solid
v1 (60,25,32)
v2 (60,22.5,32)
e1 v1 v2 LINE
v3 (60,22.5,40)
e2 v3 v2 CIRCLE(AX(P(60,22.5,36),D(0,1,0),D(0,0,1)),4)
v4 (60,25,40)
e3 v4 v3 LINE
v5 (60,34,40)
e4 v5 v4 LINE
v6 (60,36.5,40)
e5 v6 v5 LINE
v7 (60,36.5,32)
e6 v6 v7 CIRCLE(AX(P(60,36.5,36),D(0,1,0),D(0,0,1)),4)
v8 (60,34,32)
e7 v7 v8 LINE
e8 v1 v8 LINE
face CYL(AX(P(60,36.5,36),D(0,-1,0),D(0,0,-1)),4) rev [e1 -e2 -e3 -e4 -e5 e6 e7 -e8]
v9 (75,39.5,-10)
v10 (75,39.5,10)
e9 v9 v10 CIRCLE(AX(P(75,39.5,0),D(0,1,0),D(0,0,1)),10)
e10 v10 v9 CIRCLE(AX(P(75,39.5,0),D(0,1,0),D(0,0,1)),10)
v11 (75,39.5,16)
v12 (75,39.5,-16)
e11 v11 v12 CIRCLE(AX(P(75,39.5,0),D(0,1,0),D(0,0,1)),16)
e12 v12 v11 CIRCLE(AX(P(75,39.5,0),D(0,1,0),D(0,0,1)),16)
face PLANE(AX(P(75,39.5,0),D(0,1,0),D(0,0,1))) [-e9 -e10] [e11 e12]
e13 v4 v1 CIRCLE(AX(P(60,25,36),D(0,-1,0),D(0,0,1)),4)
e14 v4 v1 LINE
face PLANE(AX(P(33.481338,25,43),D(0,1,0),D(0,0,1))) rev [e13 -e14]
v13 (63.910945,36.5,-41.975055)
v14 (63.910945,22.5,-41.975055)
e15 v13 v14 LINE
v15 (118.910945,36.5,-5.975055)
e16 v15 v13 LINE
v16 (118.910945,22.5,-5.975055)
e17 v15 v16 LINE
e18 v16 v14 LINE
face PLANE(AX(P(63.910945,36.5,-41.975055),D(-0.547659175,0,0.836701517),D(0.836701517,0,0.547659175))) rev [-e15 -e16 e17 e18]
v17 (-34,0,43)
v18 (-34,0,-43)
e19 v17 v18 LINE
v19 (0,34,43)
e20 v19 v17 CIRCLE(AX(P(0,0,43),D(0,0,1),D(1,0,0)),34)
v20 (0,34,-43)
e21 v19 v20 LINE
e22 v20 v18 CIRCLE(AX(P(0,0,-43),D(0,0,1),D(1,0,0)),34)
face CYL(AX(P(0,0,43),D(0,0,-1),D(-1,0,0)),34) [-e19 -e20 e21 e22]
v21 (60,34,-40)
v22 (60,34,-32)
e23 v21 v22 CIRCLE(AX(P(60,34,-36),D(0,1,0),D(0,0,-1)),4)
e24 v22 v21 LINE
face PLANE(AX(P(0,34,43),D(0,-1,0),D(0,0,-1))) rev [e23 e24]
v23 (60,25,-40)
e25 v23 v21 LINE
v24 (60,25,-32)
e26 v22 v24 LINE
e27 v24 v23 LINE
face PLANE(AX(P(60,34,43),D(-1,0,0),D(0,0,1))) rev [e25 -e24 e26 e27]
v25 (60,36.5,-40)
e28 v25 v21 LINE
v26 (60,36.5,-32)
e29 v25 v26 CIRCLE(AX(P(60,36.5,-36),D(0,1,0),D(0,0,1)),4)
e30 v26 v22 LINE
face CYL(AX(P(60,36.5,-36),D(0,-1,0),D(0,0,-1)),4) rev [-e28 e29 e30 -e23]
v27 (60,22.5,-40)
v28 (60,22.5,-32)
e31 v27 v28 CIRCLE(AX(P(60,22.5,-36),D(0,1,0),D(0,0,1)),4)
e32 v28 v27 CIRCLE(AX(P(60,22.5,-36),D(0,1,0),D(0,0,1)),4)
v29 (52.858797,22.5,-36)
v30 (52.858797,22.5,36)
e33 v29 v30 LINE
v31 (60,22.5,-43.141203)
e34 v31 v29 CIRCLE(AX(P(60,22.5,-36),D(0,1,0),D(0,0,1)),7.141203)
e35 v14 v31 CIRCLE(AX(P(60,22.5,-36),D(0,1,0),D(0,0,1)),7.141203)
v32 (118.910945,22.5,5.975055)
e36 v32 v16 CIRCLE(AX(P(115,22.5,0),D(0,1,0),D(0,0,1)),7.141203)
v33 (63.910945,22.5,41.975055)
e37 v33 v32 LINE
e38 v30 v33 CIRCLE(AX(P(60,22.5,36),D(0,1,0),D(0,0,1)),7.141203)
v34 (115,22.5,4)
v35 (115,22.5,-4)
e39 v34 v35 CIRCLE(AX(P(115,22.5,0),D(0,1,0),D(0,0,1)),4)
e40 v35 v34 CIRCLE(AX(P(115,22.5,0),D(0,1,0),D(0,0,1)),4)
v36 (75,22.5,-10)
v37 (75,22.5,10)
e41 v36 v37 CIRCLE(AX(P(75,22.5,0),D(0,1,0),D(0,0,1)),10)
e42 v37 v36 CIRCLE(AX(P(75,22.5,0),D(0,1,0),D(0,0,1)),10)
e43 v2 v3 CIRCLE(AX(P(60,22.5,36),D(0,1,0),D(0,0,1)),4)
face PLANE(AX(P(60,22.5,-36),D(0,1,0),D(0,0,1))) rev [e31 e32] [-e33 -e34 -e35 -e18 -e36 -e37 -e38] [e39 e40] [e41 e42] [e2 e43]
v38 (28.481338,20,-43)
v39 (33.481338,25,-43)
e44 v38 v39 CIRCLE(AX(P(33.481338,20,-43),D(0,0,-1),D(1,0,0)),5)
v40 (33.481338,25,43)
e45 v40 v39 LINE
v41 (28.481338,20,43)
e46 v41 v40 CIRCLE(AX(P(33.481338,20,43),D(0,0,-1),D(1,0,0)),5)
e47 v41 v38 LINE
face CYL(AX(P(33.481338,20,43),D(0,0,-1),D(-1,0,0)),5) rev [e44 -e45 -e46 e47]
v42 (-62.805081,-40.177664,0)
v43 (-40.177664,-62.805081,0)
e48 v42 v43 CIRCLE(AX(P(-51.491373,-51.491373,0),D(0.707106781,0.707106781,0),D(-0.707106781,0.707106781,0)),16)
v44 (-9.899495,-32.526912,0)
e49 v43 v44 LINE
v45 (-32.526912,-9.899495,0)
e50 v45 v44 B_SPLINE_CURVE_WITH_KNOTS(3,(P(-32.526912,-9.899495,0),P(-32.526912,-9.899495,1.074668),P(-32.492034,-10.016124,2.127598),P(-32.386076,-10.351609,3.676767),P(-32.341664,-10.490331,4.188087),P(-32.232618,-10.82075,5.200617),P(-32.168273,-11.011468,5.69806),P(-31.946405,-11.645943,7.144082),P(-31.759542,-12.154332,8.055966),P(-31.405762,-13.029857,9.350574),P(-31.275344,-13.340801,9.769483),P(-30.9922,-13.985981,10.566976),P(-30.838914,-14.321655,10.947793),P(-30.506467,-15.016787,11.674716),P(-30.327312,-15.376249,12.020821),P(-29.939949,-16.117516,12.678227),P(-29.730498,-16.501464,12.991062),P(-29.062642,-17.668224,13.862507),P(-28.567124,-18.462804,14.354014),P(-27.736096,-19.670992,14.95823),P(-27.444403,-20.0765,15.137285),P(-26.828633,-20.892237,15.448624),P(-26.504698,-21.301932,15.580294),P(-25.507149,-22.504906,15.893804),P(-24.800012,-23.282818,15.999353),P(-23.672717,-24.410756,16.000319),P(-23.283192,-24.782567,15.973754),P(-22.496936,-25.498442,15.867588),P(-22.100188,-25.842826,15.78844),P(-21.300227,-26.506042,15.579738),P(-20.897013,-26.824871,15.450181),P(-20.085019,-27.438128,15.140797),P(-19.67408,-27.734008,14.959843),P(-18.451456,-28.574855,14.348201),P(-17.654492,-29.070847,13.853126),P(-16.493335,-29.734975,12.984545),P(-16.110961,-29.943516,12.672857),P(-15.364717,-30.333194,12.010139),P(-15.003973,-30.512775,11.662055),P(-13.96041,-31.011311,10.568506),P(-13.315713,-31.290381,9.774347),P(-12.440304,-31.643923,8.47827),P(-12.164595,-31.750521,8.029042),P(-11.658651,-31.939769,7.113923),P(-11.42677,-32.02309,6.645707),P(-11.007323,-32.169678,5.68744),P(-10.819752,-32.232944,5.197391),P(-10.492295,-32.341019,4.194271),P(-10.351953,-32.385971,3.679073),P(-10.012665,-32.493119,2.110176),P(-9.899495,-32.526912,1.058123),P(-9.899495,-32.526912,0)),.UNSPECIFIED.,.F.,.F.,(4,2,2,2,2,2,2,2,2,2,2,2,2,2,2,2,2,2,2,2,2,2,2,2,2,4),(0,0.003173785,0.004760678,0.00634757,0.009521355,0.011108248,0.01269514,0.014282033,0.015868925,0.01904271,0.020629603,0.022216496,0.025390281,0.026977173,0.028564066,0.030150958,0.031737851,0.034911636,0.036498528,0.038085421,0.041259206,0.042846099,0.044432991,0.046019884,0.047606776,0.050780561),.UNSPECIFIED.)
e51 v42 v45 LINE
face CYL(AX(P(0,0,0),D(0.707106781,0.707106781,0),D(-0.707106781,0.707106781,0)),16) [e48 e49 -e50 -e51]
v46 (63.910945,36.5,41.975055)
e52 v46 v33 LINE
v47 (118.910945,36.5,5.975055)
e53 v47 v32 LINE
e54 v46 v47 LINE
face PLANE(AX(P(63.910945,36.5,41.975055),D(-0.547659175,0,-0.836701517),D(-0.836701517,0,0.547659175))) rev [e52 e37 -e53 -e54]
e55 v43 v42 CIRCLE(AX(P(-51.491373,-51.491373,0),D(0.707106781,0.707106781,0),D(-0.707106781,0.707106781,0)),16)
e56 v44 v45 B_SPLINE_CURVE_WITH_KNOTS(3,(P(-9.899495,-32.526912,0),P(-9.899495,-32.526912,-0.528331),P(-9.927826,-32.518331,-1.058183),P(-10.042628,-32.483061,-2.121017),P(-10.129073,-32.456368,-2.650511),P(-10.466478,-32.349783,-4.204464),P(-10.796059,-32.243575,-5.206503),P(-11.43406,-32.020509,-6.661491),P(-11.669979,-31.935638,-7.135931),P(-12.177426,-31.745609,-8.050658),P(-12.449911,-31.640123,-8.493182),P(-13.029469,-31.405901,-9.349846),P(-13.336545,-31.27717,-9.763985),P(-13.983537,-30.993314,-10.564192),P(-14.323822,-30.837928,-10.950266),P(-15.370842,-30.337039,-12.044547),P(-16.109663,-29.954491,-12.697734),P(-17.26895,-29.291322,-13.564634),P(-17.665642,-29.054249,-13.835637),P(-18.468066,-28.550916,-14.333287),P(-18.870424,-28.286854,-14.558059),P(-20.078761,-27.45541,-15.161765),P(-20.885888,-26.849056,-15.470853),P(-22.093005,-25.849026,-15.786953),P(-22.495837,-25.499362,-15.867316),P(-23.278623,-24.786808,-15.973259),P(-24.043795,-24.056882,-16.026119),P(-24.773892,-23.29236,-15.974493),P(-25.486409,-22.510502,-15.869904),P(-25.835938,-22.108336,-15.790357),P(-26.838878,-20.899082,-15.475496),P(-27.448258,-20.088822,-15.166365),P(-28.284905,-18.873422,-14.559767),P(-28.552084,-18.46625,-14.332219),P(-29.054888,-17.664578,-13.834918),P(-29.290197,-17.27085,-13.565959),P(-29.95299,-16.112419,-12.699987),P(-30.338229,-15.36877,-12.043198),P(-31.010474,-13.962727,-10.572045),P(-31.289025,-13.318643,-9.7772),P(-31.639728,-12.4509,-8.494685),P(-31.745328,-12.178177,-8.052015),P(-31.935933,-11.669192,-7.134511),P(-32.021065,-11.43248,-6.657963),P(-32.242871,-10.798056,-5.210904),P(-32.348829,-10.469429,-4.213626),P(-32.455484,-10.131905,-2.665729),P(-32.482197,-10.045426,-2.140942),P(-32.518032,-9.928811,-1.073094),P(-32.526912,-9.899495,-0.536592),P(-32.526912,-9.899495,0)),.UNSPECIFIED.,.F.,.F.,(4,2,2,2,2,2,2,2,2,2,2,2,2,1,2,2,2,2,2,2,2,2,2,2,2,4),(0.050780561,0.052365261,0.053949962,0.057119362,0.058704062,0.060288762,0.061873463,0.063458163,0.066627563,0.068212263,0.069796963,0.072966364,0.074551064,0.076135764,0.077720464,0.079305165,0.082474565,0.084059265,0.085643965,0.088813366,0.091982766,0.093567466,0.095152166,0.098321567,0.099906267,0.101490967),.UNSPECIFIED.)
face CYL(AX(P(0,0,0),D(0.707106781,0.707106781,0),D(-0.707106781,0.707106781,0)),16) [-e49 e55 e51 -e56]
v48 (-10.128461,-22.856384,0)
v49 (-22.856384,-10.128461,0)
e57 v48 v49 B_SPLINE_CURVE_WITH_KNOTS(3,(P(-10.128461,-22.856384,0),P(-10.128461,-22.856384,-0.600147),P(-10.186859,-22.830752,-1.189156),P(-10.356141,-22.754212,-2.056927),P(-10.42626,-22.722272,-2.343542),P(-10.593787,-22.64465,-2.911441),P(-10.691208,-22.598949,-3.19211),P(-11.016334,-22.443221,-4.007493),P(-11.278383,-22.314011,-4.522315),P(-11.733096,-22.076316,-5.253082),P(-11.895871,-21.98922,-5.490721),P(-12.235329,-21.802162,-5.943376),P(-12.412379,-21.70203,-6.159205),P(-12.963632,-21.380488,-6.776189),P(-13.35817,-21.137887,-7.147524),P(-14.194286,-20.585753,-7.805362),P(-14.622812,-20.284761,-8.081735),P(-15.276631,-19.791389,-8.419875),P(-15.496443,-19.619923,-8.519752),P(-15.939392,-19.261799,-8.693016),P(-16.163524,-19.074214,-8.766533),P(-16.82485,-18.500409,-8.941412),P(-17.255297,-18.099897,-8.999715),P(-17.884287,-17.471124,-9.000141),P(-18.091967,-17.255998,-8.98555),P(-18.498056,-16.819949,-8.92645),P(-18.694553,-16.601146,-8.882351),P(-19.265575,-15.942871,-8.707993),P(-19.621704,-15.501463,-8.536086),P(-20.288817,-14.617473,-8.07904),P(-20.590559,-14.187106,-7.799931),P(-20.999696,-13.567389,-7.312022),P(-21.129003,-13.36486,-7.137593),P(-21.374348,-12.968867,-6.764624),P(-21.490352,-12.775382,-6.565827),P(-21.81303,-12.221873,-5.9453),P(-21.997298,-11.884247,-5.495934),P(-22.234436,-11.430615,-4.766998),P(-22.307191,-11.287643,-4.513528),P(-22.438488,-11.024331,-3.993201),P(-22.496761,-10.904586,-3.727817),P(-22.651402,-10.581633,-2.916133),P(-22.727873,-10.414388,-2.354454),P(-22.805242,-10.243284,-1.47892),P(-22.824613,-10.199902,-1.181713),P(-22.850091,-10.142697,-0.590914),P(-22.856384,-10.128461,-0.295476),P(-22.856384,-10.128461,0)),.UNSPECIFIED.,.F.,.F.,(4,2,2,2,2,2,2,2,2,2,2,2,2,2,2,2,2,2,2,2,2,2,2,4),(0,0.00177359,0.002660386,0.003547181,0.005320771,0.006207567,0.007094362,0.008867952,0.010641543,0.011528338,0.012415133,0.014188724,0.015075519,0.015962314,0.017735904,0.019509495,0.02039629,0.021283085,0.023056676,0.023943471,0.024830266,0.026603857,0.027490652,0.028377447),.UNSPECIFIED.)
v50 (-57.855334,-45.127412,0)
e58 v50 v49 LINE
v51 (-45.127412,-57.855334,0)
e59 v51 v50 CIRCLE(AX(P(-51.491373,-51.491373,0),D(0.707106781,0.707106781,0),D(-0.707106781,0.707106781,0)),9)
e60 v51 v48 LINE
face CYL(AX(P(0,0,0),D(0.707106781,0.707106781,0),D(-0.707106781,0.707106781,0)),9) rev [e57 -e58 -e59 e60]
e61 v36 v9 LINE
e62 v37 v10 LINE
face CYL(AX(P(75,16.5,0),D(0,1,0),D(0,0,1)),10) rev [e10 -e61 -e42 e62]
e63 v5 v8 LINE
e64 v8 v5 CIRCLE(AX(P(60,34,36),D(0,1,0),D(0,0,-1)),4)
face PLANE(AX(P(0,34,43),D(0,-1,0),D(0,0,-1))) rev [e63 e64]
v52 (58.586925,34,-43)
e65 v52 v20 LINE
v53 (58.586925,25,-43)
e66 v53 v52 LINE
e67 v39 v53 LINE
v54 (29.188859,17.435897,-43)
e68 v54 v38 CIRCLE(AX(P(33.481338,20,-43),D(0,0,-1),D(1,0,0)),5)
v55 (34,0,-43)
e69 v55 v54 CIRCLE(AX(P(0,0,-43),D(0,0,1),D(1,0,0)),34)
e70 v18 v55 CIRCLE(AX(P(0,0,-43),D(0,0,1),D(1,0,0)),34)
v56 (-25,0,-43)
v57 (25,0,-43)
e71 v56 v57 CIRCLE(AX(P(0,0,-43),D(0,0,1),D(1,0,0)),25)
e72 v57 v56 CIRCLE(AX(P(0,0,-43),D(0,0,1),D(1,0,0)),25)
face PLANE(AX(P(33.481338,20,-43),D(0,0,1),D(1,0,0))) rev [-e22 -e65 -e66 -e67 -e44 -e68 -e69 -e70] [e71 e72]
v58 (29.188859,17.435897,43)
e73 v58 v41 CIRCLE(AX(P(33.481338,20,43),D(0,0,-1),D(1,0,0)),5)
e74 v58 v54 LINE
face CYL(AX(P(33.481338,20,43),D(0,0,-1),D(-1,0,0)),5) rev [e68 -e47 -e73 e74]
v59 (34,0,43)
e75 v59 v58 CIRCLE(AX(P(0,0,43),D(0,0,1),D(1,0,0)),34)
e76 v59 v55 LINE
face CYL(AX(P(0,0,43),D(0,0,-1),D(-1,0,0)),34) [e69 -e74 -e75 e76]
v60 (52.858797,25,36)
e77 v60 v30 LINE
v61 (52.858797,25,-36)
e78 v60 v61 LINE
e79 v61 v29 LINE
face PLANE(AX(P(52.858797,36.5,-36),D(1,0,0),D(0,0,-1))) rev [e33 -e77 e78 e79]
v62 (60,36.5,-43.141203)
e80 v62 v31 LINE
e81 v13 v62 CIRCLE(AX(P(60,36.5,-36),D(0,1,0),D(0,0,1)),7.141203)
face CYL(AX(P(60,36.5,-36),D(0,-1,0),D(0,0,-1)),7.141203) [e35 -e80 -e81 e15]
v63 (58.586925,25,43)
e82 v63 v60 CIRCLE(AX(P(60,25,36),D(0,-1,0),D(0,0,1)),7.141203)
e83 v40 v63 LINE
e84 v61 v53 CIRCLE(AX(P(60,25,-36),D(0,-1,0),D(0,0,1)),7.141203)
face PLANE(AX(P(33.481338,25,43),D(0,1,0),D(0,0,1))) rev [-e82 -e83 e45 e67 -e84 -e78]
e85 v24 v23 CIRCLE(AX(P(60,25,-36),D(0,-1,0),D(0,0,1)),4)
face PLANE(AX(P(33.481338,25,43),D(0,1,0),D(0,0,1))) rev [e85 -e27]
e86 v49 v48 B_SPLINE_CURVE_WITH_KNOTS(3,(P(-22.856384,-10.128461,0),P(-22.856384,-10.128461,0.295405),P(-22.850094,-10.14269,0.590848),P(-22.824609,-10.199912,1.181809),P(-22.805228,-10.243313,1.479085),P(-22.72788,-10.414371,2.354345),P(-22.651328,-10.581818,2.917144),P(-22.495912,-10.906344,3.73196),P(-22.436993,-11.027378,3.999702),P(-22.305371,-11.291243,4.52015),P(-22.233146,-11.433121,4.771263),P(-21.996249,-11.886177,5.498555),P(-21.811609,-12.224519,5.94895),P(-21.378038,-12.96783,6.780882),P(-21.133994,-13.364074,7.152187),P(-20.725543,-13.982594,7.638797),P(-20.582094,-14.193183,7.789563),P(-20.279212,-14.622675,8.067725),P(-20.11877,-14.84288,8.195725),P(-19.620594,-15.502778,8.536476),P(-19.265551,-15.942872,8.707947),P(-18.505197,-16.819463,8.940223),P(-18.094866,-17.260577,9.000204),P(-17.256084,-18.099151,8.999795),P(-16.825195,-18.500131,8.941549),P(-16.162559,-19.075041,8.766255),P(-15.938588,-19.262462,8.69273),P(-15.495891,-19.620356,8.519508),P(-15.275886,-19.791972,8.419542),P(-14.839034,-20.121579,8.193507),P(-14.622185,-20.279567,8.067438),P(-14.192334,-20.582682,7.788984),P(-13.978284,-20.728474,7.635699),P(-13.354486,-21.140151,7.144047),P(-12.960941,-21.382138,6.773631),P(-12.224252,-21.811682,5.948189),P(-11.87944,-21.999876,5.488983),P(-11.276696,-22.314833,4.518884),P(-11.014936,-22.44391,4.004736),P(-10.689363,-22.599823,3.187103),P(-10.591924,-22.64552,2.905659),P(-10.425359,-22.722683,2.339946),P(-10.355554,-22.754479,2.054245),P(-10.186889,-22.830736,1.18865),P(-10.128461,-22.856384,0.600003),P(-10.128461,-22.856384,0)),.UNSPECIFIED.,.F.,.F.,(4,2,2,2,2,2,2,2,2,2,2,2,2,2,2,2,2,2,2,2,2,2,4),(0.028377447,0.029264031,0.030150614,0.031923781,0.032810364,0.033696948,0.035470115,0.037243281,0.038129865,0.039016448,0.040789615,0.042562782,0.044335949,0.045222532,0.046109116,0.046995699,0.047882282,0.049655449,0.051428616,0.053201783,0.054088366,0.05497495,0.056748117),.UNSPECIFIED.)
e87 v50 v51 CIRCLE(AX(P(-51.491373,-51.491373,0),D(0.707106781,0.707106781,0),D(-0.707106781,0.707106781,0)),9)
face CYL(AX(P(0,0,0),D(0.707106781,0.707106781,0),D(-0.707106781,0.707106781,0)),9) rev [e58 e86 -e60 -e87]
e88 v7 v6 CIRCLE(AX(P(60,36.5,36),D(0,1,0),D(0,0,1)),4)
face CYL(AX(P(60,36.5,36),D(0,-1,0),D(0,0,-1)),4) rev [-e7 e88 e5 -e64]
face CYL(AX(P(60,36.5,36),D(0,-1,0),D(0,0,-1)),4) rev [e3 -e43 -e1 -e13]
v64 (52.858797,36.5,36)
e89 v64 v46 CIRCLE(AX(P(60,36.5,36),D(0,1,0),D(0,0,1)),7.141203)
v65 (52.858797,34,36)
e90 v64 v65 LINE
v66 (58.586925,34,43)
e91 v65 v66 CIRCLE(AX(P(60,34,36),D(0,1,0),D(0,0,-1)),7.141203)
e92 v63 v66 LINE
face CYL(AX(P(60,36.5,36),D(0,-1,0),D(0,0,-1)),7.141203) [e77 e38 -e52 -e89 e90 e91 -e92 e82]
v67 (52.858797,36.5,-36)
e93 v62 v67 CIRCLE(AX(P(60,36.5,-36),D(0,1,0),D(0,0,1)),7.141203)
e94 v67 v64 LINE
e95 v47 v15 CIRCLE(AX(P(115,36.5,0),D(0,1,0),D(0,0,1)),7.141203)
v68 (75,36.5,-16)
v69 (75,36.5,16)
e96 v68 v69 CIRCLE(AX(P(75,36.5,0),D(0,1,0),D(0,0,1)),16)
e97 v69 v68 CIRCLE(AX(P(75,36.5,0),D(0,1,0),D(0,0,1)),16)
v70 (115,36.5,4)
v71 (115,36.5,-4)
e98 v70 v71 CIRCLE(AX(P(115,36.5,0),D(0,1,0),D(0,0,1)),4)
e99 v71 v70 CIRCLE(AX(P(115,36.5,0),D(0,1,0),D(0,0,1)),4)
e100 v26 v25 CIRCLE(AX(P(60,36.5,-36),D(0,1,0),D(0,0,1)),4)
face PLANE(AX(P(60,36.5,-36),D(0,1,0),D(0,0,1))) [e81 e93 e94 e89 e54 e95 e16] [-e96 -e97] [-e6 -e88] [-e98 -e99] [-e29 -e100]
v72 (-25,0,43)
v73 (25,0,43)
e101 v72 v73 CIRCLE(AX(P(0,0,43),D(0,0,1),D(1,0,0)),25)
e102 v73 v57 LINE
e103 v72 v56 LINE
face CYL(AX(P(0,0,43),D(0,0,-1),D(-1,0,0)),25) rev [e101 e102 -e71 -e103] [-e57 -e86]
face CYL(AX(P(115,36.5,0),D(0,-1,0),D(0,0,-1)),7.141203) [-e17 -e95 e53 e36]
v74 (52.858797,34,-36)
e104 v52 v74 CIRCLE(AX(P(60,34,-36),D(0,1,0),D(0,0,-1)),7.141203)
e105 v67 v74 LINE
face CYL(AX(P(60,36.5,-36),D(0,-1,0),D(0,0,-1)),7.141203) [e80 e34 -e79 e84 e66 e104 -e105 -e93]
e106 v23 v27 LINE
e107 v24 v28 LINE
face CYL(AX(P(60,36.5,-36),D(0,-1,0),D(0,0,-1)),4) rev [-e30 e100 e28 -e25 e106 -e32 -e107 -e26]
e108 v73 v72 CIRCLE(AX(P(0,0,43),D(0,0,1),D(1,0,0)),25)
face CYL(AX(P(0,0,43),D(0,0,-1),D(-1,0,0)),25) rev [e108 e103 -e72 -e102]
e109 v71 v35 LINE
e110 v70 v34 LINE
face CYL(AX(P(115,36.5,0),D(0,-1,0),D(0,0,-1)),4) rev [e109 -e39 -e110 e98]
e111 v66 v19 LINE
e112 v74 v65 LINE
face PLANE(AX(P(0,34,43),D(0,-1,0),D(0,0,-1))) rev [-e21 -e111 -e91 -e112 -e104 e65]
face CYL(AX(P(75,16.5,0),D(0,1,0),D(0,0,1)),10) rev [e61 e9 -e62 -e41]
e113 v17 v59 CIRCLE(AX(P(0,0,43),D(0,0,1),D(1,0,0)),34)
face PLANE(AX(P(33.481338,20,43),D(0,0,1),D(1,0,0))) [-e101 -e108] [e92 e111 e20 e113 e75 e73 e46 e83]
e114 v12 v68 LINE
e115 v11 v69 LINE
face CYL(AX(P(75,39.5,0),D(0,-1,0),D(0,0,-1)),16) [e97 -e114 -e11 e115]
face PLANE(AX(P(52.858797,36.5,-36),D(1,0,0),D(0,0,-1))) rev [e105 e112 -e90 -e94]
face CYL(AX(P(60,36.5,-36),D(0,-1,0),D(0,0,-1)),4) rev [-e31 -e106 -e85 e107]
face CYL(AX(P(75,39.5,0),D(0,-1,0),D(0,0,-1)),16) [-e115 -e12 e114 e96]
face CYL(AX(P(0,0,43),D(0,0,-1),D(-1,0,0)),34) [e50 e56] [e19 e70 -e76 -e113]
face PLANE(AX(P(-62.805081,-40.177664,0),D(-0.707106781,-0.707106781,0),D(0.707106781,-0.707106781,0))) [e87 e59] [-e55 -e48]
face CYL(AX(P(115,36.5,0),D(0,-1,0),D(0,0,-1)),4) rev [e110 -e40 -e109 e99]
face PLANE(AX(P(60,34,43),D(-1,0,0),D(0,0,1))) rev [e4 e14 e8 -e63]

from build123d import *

# Parameters (mm, degrees)
RING_HUB_PROFILE_R       = 25
RING_HUB_DEPTH           = 43
FLANGE_PROFILE_3_HOLES_R = 4
TRIANGULAR_FLANGE_DEPTH  = 7
BOSS_BORE_PROFILE_R      = 10
BOSS_BORE_DEPTH          = 13
FLANGE_START             = 3
FLANGE_BOSS_PROFILE_R    = 16
FLANGE_BOSS_PROFILE_R_2  = 10
FLANGE_BOSS_32_DEPTH     = 3
HUB_SLIT_PROFILE_R       = 9
HUB_SLIT_CUT_DEPTH       = 67.5


with BuildPart() as part:
    # Ring Hub Profile → Ring Hub (new, symmetric)
    with BuildSketch(Plane.XY):
        with BuildLine():
            Line((0, 34), (60, 34))
            Line((60, 34), (60, 25))
            Line((60, 25), (33.481338086, 25))
            ThreePointArc((33.481338086, 25), (29.132745622, 22.467740584), (29.188858844, 17.435897436))
            ThreePointArc((29.188858844, 17.435897436), (-16.780635971, -29.570428749), (0, 34))
        make_face()
        Circle(RING_HUB_PROFILE_R, mode=Mode.SUBTRACT)
    extrude(amount=RING_HUB_DEPTH, both=True)

    # Flange Profile 3 Holes → Triangular Flange (add, symmetric)
    with BuildSketch(Plane(origin=(0, 29.5, 0), x_dir=(1, 0, 0), z_dir=(0, 1, 0))):
        with BuildLine():
            Line((63.910945409, 41.975055486), (118.910945409, 5.975055486))
            ThreePointArc((118.910945409, 5.975055486), (122.141203123, 0), (118.910945409, -5.975055486))
            Line((118.910945409, -5.975055486), (63.910945409, -41.975055486))
            ThreePointArc((63.910945409, -41.975055486), (56.603831094, -42.281943872), (52.858796877, -36))
            Line((52.858796877, -36), (52.858796877, 36))
            ThreePointArc((52.858796877, 36), (56.603831094, 42.281943872), (63.910945409, 41.975055486))
        make_face()
        with Locations(Location((60, 36, 0), (0, 0, 270))):
            Circle(FLANGE_PROFILE_3_HOLES_R, mode=Mode.SUBTRACT)
        with Locations(Location((60, -36, 0), (0, 0, 270))):
            Circle(FLANGE_PROFILE_3_HOLES_R, mode=Mode.SUBTRACT)
        with Locations(Location((115, 0, 0), (0, 0, 270))):
            Circle(FLANGE_PROFILE_3_HOLES_R, mode=Mode.SUBTRACT)
    extrude(amount=TRIANGULAR_FLANGE_DEPTH, both=True)

    # Boss Bore Profile → Boss Bore (cut, symmetric)
    with BuildSketch(Plane(origin=(0, 29.5, 0), x_dir=(1, 0, 0), z_dir=(0, 1, 0))):
        with Locations(Location((75, 0, 0), (0, 0, 270))):
            Circle(BOSS_BORE_PROFILE_R)
    extrude(amount=BOSS_BORE_DEPTH, both=True, mode=Mode.SUBTRACT)

    # Flange Boss Profile → Flange Boss Ø32 (add)
    with BuildSketch(Plane(origin=(0, 36.5, 0), x_dir=(1, 0, 0), z_dir=(0, 1, 0)).offset(FLANGE_START)):
        with Locations(Location((75, 0, 0), (0, 0, 270))):
            Circle(FLANGE_BOSS_PROFILE_R)
        with Locations(Location((75, 0, 0), (0, 0, 270))):
            Circle(FLANGE_BOSS_PROFILE_R_2, mode=Mode.SUBTRACT)
    extrude(amount=-FLANGE_BOSS_32_DEPTH)

    # Hub Revolve Profile → Hub Revolved Feature (revolve)
    with BuildSketch(Plane.XY):
        with BuildLine():
            Line((-32.526911935, -9.899494937), (-62.805081277, -40.177664279))
            Line((-62.805081277, -40.177664279), (-57.855333809, -45.127411748))
            Line((-57.855333809, -45.127411748), (-29.548007269, -16.820085208))
            ThreePointArc((-29.548007269, -16.820085208), (-31.229754097, -13.442561476), (-32.526911935, -9.899494937))
        make_face()
    revolve(axis=Axis((0, 0, 0), (-0.7071067811865461, -0.707106781186549, 0)))

    # Hub Slit Profile → Hub Slit Cut (cut, symmetric)
    with BuildSketch(Plane(origin=(-51.491372778, -51.491372778, 0), x_dir=(0, 0, 1), z_dir=(-0.7071067811865462, -0.7071067811865489, 0))):
        with Locations(Location((0, 0, 0), (0, 0, 90))):
            Circle(HUB_SLIT_PROFILE_R)
    extrude(amount=HUB_SLIT_CUT_DEPTH, both=True, mode=Mode.SUBTRACT)


solid = part.part
